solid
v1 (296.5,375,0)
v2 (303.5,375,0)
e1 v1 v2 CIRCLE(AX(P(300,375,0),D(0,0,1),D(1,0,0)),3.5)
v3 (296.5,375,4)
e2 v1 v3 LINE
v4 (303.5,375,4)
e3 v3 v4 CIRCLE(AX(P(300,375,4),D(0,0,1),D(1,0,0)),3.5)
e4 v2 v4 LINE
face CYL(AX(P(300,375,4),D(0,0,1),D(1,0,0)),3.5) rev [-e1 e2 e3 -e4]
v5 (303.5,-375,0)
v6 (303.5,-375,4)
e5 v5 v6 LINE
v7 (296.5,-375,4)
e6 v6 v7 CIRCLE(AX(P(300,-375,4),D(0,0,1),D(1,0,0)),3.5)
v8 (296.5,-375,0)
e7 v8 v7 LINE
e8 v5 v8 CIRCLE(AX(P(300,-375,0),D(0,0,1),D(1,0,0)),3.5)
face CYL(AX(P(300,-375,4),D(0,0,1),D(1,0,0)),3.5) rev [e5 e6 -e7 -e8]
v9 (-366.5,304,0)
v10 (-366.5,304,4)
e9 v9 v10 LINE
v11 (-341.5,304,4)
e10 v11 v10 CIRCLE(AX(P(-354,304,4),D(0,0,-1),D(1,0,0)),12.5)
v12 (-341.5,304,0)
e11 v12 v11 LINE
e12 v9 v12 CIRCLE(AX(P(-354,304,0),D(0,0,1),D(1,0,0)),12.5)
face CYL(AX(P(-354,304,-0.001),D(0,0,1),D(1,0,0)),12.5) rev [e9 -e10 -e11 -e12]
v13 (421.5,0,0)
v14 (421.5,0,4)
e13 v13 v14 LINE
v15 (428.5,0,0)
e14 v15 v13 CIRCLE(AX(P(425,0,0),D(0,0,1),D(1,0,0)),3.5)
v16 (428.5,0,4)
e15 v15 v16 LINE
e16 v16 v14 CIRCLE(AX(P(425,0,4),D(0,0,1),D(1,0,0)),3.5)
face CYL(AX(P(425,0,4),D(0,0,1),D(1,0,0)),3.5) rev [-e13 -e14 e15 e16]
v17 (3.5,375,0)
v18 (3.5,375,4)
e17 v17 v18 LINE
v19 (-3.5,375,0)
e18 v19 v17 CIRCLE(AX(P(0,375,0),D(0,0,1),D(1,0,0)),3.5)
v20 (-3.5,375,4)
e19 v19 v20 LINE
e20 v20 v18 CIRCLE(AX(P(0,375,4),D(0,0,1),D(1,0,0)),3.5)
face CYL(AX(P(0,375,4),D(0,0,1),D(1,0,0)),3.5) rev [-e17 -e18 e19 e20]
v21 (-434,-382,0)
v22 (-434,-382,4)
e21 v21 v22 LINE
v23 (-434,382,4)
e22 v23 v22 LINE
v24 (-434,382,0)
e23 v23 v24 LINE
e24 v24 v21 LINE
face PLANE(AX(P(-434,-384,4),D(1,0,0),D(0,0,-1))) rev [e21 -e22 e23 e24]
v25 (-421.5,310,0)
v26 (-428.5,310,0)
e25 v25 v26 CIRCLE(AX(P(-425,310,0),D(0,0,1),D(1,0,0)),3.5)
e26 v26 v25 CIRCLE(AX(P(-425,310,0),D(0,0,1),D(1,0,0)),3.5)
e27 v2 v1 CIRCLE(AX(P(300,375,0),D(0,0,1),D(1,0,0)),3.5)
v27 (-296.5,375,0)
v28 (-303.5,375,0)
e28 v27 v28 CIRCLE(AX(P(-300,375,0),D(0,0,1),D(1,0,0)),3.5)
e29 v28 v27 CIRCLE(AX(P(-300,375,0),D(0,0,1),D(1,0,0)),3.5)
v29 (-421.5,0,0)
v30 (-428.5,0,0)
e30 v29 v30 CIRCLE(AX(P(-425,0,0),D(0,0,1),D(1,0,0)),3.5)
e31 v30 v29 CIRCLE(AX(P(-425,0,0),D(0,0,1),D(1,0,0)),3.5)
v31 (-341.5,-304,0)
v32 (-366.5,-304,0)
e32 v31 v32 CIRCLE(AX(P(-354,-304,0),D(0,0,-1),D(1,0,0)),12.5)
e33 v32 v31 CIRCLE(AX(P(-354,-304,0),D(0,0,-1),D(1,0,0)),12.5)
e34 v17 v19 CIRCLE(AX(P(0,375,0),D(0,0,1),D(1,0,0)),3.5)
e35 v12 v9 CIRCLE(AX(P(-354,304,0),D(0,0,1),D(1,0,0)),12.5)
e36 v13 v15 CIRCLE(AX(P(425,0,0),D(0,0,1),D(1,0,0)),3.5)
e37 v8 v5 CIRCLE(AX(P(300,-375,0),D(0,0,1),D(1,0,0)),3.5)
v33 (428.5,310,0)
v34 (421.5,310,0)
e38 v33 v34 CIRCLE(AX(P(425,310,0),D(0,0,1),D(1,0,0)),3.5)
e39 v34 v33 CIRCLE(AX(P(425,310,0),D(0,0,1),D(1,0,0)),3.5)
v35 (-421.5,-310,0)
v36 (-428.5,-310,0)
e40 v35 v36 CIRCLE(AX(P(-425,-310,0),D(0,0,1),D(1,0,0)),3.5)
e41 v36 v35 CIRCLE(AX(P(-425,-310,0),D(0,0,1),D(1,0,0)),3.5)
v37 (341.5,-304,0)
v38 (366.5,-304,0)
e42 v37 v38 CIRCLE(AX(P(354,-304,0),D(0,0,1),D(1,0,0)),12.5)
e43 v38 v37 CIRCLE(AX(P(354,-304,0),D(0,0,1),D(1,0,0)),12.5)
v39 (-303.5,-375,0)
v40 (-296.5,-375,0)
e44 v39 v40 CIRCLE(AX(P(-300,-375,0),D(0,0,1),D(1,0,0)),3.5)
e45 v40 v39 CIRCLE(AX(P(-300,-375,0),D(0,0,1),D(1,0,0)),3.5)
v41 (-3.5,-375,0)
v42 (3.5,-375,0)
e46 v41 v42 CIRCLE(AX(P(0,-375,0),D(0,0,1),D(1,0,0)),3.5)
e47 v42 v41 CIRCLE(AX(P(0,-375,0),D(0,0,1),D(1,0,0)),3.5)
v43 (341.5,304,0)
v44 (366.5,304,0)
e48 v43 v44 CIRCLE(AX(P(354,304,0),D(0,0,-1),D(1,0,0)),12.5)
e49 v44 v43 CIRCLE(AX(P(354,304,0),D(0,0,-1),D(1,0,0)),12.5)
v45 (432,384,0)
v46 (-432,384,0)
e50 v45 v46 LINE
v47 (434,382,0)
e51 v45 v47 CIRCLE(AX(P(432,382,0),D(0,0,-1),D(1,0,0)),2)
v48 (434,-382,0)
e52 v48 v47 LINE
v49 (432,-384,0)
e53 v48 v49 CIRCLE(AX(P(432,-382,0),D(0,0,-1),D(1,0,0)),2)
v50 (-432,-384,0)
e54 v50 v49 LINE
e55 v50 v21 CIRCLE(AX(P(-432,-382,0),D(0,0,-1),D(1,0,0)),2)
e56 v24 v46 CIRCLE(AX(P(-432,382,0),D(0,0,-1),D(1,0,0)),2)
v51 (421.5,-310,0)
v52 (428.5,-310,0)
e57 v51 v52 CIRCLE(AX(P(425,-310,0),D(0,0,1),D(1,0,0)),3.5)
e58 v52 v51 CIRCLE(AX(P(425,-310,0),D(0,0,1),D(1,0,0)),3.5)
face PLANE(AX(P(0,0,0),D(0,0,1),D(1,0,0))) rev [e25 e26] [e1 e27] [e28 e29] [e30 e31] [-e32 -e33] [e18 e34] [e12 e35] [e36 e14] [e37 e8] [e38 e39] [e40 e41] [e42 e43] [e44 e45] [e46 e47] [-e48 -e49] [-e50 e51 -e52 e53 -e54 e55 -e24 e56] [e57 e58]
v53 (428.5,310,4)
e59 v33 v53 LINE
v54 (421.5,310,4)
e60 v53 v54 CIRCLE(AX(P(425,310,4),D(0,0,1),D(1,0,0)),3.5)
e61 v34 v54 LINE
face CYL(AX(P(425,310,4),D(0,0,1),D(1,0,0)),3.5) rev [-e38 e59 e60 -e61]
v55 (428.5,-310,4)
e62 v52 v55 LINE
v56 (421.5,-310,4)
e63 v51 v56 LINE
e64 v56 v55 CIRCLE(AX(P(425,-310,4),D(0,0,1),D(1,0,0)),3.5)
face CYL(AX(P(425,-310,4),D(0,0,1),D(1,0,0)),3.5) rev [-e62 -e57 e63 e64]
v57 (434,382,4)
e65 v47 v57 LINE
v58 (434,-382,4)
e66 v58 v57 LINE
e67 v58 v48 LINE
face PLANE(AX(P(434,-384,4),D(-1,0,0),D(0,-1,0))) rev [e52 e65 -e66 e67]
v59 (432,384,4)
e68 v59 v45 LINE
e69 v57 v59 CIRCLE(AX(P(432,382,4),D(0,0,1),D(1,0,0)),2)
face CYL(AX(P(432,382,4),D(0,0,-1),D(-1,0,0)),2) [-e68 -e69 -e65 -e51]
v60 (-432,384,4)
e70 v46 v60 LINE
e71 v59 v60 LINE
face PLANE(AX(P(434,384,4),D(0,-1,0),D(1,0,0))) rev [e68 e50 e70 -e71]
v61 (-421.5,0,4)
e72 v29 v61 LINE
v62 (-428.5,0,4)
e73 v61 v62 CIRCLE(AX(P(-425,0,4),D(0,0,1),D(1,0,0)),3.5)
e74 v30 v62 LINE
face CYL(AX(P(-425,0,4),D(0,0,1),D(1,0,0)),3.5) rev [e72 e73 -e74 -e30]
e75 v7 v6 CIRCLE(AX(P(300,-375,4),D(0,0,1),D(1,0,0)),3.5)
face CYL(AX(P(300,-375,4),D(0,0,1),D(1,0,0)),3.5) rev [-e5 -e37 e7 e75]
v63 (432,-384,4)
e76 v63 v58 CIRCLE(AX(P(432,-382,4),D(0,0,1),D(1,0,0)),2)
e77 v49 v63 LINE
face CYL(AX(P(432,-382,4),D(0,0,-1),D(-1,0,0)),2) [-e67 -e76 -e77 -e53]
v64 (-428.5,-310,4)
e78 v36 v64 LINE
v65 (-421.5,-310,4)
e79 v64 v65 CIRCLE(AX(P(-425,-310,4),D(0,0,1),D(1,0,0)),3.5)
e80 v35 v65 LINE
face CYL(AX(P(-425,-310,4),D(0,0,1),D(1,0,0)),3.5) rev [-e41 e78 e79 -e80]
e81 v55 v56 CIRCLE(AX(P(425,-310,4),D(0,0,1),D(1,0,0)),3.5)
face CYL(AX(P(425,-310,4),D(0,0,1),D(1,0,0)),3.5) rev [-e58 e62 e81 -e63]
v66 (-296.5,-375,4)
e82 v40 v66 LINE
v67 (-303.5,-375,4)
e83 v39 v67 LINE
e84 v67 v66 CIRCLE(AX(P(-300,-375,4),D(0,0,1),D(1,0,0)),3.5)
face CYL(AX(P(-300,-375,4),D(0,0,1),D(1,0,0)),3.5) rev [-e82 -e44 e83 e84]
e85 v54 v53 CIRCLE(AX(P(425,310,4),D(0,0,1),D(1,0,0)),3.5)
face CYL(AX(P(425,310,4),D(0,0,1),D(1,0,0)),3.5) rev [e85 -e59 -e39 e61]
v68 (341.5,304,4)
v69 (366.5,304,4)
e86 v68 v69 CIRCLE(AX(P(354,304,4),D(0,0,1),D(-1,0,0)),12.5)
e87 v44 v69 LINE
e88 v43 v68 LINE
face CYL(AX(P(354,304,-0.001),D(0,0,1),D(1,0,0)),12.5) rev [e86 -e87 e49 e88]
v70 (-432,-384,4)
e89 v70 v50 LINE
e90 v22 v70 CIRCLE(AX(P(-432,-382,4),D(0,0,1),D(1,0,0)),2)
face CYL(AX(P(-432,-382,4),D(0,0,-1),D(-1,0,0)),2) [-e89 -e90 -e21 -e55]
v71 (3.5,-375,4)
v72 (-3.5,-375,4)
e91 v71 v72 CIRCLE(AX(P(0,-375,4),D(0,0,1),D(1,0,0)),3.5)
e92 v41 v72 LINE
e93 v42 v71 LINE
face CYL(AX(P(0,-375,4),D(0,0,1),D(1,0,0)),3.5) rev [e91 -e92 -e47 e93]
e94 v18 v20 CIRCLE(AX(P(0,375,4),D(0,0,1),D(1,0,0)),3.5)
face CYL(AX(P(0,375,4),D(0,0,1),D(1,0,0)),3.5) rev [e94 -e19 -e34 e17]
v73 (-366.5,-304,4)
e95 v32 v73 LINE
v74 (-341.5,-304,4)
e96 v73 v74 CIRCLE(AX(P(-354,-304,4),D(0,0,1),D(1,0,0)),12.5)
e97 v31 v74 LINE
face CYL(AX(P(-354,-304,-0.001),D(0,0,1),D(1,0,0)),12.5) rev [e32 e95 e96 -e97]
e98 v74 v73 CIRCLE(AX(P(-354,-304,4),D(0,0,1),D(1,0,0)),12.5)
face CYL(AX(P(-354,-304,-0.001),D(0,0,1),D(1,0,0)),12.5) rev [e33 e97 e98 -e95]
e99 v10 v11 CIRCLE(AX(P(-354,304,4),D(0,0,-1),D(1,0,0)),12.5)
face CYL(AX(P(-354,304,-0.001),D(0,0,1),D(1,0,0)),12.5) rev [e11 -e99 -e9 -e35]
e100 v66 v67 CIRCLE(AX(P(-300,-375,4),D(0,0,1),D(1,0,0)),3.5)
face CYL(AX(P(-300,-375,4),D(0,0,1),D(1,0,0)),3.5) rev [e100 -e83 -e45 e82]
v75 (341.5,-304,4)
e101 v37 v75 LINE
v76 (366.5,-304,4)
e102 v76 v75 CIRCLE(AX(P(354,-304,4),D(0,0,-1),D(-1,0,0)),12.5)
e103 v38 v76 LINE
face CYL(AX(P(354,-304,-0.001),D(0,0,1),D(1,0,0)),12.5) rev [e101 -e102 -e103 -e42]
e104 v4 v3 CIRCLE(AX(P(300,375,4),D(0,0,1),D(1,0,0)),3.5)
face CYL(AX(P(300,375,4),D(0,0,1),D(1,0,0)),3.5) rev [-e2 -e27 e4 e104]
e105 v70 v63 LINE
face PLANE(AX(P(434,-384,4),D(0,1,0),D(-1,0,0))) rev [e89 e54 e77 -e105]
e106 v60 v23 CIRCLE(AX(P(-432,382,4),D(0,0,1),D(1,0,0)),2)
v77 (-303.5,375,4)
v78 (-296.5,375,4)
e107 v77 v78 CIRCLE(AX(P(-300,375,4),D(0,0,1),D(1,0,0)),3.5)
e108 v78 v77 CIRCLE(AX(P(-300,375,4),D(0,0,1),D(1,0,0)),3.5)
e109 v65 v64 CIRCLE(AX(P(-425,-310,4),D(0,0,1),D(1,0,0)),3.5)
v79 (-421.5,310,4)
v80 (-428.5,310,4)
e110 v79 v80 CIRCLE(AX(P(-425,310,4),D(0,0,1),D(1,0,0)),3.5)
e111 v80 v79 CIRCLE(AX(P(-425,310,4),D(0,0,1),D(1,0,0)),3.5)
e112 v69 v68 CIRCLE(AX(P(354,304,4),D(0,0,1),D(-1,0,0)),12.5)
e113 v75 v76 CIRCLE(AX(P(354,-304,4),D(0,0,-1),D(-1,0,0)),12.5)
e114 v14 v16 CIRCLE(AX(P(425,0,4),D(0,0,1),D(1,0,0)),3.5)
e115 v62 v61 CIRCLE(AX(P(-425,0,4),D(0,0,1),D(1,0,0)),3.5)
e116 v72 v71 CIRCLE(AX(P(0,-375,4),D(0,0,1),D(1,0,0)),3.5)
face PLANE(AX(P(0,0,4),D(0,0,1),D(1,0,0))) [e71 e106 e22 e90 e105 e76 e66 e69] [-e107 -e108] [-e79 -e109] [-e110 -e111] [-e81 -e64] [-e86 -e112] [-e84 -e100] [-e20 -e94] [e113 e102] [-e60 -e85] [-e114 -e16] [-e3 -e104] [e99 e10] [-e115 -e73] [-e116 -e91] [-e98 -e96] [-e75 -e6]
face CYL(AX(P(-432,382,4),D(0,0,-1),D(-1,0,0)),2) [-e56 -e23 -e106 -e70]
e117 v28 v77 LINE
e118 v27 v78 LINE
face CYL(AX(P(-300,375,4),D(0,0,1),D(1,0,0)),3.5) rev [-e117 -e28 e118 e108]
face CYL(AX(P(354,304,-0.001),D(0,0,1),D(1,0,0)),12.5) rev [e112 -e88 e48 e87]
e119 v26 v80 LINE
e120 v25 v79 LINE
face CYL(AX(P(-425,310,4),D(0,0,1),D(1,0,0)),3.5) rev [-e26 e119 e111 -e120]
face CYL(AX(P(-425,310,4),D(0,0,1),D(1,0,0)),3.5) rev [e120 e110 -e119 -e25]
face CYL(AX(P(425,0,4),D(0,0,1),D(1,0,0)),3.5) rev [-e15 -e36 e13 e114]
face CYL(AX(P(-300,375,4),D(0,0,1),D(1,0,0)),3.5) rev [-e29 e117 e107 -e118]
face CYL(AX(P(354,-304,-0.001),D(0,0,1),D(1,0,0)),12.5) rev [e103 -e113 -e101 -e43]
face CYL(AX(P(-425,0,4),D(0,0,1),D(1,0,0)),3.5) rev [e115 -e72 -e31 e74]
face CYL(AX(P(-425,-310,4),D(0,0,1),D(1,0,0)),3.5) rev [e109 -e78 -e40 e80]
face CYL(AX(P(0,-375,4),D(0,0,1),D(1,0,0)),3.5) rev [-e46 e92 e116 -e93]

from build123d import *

# Parameters (mm, degrees)
SKETCH_1_W               = 868
SKETCH_1_H               = 768
EXTRUDE_1_DEPTH          = 4
FILLET_1_R               = 2
HOLE_WIZARD_M6_1_D       = 7
HOLE_WIZARD_M6_2_D       = 7
CUT_EXTRUDE_1_REACH      = 581.507
SKETCH_7_R               = 12.5
MIRROR_5_COPY_1_REACH    = 581.507
MIRROR_5_COPY_1_SKETCH_R = 12.5


with BuildPart() as part:
    # 草图1 → 凸台-拉伸1 (new body)
    with BuildSketch(Plane.XY):
        Rectangle(SKETCH_1_W, SKETCH_1_H)
    extrude(amount=EXTRUDE_1_DEPTH)

    # 圆角1
    fillet_1_edges = [part.edges().sort_by_distance(p)[0] for p in [
        (-434, 384, 2),
        (434, 384, 2),
        (434, -384, 2),
        (-434, -384, 2),
    ]]
    fillet(fillet_1_edges, radius=FILLET_1_R)

    # M6 间隙孔1 (through all)
    with Locations(Plane.XY.offset(4)):
        with Locations((-425, 310), (-425, -310), (-425, 0)):
            hole_wizard_m6_1 = Hole(HOLE_WIZARD_M6_1_D / 2)

    # 镜向2: M6 间隙孔1 across plane
    add(hole_wizard_m6_1.mirror(Plane(origin=(0, 0, 0), x_dir=(0, 0, 1), z_dir=(1, 0, 0))), mode=Mode.SUBTRACT)

    # M6 间隙孔2 (through all)
    with Locations(Plane.XY.offset(4)):
        with Locations((-300, 375), (300, 375), (0, 375)):
            hole_wizard_m6_2 = Hole(HOLE_WIZARD_M6_2_D / 2)

    # 镜向3: M6 间隙孔2 across plane
    add(hole_wizard_m6_2.mirror(Plane.ZX), mode=Mode.SUBTRACT)

    # 草图7 → 切除-拉伸1 (cut, up to next)
    with BuildSketch(Plane.XY.offset(4), mode=Mode.PRIVATE) as cut_extrude_1_sk1:
        with Locations((-354, -304)):
            Circle(SKETCH_7_R)
    cut_extrude_1_tool1 = extrude(cut_extrude_1_sk1.sketch, amount=-CUT_EXTRUDE_1_REACH, mode=Mode.PRIVATE) & part.part
    cut_extrude_1 = cut_extrude_1_tool1.solids().sort_by_distance((-354, -304, 4))[0]
    add(cut_extrude_1, mode=Mode.SUBTRACT)

    # 镜向4: 切除-拉伸1 across plane
    add(cut_extrude_1.mirror(Plane(origin=(0, 0, 0), x_dir=(0, 0, 1), z_dir=(1, 0, 0))), mode=Mode.SUBTRACT)

    # 镜向5: 切除-拉伸1 across plane
    add(cut_extrude_1.mirror(Plane.ZX), mode=Mode.SUBTRACT)

    # 镜向5 copy 1 sketch → 镜向5 copy 1 (cut, up to next)
    with BuildSketch(Plane(origin=(0, 0, 4), x_dir=(-1, 0, 0), z_dir=(0, 0, 1)), mode=Mode.PRIVATE) as mirror_5_copy_1_sk1:
        with Locations((-354, -304)):
            Circle(MIRROR_5_COPY_1_SKETCH_R)
    mirror_5_copy_1_tool1 = extrude(mirror_5_copy_1_sk1.sketch, amount=-MIRROR_5_COPY_1_REACH, mode=Mode.PRIVATE) & part.part
    add(mirror_5_copy_1_tool1.solids().sort_by_distance((354, 304, 4))[0], mode=Mode.SUBTRACT)


solid = part.part
